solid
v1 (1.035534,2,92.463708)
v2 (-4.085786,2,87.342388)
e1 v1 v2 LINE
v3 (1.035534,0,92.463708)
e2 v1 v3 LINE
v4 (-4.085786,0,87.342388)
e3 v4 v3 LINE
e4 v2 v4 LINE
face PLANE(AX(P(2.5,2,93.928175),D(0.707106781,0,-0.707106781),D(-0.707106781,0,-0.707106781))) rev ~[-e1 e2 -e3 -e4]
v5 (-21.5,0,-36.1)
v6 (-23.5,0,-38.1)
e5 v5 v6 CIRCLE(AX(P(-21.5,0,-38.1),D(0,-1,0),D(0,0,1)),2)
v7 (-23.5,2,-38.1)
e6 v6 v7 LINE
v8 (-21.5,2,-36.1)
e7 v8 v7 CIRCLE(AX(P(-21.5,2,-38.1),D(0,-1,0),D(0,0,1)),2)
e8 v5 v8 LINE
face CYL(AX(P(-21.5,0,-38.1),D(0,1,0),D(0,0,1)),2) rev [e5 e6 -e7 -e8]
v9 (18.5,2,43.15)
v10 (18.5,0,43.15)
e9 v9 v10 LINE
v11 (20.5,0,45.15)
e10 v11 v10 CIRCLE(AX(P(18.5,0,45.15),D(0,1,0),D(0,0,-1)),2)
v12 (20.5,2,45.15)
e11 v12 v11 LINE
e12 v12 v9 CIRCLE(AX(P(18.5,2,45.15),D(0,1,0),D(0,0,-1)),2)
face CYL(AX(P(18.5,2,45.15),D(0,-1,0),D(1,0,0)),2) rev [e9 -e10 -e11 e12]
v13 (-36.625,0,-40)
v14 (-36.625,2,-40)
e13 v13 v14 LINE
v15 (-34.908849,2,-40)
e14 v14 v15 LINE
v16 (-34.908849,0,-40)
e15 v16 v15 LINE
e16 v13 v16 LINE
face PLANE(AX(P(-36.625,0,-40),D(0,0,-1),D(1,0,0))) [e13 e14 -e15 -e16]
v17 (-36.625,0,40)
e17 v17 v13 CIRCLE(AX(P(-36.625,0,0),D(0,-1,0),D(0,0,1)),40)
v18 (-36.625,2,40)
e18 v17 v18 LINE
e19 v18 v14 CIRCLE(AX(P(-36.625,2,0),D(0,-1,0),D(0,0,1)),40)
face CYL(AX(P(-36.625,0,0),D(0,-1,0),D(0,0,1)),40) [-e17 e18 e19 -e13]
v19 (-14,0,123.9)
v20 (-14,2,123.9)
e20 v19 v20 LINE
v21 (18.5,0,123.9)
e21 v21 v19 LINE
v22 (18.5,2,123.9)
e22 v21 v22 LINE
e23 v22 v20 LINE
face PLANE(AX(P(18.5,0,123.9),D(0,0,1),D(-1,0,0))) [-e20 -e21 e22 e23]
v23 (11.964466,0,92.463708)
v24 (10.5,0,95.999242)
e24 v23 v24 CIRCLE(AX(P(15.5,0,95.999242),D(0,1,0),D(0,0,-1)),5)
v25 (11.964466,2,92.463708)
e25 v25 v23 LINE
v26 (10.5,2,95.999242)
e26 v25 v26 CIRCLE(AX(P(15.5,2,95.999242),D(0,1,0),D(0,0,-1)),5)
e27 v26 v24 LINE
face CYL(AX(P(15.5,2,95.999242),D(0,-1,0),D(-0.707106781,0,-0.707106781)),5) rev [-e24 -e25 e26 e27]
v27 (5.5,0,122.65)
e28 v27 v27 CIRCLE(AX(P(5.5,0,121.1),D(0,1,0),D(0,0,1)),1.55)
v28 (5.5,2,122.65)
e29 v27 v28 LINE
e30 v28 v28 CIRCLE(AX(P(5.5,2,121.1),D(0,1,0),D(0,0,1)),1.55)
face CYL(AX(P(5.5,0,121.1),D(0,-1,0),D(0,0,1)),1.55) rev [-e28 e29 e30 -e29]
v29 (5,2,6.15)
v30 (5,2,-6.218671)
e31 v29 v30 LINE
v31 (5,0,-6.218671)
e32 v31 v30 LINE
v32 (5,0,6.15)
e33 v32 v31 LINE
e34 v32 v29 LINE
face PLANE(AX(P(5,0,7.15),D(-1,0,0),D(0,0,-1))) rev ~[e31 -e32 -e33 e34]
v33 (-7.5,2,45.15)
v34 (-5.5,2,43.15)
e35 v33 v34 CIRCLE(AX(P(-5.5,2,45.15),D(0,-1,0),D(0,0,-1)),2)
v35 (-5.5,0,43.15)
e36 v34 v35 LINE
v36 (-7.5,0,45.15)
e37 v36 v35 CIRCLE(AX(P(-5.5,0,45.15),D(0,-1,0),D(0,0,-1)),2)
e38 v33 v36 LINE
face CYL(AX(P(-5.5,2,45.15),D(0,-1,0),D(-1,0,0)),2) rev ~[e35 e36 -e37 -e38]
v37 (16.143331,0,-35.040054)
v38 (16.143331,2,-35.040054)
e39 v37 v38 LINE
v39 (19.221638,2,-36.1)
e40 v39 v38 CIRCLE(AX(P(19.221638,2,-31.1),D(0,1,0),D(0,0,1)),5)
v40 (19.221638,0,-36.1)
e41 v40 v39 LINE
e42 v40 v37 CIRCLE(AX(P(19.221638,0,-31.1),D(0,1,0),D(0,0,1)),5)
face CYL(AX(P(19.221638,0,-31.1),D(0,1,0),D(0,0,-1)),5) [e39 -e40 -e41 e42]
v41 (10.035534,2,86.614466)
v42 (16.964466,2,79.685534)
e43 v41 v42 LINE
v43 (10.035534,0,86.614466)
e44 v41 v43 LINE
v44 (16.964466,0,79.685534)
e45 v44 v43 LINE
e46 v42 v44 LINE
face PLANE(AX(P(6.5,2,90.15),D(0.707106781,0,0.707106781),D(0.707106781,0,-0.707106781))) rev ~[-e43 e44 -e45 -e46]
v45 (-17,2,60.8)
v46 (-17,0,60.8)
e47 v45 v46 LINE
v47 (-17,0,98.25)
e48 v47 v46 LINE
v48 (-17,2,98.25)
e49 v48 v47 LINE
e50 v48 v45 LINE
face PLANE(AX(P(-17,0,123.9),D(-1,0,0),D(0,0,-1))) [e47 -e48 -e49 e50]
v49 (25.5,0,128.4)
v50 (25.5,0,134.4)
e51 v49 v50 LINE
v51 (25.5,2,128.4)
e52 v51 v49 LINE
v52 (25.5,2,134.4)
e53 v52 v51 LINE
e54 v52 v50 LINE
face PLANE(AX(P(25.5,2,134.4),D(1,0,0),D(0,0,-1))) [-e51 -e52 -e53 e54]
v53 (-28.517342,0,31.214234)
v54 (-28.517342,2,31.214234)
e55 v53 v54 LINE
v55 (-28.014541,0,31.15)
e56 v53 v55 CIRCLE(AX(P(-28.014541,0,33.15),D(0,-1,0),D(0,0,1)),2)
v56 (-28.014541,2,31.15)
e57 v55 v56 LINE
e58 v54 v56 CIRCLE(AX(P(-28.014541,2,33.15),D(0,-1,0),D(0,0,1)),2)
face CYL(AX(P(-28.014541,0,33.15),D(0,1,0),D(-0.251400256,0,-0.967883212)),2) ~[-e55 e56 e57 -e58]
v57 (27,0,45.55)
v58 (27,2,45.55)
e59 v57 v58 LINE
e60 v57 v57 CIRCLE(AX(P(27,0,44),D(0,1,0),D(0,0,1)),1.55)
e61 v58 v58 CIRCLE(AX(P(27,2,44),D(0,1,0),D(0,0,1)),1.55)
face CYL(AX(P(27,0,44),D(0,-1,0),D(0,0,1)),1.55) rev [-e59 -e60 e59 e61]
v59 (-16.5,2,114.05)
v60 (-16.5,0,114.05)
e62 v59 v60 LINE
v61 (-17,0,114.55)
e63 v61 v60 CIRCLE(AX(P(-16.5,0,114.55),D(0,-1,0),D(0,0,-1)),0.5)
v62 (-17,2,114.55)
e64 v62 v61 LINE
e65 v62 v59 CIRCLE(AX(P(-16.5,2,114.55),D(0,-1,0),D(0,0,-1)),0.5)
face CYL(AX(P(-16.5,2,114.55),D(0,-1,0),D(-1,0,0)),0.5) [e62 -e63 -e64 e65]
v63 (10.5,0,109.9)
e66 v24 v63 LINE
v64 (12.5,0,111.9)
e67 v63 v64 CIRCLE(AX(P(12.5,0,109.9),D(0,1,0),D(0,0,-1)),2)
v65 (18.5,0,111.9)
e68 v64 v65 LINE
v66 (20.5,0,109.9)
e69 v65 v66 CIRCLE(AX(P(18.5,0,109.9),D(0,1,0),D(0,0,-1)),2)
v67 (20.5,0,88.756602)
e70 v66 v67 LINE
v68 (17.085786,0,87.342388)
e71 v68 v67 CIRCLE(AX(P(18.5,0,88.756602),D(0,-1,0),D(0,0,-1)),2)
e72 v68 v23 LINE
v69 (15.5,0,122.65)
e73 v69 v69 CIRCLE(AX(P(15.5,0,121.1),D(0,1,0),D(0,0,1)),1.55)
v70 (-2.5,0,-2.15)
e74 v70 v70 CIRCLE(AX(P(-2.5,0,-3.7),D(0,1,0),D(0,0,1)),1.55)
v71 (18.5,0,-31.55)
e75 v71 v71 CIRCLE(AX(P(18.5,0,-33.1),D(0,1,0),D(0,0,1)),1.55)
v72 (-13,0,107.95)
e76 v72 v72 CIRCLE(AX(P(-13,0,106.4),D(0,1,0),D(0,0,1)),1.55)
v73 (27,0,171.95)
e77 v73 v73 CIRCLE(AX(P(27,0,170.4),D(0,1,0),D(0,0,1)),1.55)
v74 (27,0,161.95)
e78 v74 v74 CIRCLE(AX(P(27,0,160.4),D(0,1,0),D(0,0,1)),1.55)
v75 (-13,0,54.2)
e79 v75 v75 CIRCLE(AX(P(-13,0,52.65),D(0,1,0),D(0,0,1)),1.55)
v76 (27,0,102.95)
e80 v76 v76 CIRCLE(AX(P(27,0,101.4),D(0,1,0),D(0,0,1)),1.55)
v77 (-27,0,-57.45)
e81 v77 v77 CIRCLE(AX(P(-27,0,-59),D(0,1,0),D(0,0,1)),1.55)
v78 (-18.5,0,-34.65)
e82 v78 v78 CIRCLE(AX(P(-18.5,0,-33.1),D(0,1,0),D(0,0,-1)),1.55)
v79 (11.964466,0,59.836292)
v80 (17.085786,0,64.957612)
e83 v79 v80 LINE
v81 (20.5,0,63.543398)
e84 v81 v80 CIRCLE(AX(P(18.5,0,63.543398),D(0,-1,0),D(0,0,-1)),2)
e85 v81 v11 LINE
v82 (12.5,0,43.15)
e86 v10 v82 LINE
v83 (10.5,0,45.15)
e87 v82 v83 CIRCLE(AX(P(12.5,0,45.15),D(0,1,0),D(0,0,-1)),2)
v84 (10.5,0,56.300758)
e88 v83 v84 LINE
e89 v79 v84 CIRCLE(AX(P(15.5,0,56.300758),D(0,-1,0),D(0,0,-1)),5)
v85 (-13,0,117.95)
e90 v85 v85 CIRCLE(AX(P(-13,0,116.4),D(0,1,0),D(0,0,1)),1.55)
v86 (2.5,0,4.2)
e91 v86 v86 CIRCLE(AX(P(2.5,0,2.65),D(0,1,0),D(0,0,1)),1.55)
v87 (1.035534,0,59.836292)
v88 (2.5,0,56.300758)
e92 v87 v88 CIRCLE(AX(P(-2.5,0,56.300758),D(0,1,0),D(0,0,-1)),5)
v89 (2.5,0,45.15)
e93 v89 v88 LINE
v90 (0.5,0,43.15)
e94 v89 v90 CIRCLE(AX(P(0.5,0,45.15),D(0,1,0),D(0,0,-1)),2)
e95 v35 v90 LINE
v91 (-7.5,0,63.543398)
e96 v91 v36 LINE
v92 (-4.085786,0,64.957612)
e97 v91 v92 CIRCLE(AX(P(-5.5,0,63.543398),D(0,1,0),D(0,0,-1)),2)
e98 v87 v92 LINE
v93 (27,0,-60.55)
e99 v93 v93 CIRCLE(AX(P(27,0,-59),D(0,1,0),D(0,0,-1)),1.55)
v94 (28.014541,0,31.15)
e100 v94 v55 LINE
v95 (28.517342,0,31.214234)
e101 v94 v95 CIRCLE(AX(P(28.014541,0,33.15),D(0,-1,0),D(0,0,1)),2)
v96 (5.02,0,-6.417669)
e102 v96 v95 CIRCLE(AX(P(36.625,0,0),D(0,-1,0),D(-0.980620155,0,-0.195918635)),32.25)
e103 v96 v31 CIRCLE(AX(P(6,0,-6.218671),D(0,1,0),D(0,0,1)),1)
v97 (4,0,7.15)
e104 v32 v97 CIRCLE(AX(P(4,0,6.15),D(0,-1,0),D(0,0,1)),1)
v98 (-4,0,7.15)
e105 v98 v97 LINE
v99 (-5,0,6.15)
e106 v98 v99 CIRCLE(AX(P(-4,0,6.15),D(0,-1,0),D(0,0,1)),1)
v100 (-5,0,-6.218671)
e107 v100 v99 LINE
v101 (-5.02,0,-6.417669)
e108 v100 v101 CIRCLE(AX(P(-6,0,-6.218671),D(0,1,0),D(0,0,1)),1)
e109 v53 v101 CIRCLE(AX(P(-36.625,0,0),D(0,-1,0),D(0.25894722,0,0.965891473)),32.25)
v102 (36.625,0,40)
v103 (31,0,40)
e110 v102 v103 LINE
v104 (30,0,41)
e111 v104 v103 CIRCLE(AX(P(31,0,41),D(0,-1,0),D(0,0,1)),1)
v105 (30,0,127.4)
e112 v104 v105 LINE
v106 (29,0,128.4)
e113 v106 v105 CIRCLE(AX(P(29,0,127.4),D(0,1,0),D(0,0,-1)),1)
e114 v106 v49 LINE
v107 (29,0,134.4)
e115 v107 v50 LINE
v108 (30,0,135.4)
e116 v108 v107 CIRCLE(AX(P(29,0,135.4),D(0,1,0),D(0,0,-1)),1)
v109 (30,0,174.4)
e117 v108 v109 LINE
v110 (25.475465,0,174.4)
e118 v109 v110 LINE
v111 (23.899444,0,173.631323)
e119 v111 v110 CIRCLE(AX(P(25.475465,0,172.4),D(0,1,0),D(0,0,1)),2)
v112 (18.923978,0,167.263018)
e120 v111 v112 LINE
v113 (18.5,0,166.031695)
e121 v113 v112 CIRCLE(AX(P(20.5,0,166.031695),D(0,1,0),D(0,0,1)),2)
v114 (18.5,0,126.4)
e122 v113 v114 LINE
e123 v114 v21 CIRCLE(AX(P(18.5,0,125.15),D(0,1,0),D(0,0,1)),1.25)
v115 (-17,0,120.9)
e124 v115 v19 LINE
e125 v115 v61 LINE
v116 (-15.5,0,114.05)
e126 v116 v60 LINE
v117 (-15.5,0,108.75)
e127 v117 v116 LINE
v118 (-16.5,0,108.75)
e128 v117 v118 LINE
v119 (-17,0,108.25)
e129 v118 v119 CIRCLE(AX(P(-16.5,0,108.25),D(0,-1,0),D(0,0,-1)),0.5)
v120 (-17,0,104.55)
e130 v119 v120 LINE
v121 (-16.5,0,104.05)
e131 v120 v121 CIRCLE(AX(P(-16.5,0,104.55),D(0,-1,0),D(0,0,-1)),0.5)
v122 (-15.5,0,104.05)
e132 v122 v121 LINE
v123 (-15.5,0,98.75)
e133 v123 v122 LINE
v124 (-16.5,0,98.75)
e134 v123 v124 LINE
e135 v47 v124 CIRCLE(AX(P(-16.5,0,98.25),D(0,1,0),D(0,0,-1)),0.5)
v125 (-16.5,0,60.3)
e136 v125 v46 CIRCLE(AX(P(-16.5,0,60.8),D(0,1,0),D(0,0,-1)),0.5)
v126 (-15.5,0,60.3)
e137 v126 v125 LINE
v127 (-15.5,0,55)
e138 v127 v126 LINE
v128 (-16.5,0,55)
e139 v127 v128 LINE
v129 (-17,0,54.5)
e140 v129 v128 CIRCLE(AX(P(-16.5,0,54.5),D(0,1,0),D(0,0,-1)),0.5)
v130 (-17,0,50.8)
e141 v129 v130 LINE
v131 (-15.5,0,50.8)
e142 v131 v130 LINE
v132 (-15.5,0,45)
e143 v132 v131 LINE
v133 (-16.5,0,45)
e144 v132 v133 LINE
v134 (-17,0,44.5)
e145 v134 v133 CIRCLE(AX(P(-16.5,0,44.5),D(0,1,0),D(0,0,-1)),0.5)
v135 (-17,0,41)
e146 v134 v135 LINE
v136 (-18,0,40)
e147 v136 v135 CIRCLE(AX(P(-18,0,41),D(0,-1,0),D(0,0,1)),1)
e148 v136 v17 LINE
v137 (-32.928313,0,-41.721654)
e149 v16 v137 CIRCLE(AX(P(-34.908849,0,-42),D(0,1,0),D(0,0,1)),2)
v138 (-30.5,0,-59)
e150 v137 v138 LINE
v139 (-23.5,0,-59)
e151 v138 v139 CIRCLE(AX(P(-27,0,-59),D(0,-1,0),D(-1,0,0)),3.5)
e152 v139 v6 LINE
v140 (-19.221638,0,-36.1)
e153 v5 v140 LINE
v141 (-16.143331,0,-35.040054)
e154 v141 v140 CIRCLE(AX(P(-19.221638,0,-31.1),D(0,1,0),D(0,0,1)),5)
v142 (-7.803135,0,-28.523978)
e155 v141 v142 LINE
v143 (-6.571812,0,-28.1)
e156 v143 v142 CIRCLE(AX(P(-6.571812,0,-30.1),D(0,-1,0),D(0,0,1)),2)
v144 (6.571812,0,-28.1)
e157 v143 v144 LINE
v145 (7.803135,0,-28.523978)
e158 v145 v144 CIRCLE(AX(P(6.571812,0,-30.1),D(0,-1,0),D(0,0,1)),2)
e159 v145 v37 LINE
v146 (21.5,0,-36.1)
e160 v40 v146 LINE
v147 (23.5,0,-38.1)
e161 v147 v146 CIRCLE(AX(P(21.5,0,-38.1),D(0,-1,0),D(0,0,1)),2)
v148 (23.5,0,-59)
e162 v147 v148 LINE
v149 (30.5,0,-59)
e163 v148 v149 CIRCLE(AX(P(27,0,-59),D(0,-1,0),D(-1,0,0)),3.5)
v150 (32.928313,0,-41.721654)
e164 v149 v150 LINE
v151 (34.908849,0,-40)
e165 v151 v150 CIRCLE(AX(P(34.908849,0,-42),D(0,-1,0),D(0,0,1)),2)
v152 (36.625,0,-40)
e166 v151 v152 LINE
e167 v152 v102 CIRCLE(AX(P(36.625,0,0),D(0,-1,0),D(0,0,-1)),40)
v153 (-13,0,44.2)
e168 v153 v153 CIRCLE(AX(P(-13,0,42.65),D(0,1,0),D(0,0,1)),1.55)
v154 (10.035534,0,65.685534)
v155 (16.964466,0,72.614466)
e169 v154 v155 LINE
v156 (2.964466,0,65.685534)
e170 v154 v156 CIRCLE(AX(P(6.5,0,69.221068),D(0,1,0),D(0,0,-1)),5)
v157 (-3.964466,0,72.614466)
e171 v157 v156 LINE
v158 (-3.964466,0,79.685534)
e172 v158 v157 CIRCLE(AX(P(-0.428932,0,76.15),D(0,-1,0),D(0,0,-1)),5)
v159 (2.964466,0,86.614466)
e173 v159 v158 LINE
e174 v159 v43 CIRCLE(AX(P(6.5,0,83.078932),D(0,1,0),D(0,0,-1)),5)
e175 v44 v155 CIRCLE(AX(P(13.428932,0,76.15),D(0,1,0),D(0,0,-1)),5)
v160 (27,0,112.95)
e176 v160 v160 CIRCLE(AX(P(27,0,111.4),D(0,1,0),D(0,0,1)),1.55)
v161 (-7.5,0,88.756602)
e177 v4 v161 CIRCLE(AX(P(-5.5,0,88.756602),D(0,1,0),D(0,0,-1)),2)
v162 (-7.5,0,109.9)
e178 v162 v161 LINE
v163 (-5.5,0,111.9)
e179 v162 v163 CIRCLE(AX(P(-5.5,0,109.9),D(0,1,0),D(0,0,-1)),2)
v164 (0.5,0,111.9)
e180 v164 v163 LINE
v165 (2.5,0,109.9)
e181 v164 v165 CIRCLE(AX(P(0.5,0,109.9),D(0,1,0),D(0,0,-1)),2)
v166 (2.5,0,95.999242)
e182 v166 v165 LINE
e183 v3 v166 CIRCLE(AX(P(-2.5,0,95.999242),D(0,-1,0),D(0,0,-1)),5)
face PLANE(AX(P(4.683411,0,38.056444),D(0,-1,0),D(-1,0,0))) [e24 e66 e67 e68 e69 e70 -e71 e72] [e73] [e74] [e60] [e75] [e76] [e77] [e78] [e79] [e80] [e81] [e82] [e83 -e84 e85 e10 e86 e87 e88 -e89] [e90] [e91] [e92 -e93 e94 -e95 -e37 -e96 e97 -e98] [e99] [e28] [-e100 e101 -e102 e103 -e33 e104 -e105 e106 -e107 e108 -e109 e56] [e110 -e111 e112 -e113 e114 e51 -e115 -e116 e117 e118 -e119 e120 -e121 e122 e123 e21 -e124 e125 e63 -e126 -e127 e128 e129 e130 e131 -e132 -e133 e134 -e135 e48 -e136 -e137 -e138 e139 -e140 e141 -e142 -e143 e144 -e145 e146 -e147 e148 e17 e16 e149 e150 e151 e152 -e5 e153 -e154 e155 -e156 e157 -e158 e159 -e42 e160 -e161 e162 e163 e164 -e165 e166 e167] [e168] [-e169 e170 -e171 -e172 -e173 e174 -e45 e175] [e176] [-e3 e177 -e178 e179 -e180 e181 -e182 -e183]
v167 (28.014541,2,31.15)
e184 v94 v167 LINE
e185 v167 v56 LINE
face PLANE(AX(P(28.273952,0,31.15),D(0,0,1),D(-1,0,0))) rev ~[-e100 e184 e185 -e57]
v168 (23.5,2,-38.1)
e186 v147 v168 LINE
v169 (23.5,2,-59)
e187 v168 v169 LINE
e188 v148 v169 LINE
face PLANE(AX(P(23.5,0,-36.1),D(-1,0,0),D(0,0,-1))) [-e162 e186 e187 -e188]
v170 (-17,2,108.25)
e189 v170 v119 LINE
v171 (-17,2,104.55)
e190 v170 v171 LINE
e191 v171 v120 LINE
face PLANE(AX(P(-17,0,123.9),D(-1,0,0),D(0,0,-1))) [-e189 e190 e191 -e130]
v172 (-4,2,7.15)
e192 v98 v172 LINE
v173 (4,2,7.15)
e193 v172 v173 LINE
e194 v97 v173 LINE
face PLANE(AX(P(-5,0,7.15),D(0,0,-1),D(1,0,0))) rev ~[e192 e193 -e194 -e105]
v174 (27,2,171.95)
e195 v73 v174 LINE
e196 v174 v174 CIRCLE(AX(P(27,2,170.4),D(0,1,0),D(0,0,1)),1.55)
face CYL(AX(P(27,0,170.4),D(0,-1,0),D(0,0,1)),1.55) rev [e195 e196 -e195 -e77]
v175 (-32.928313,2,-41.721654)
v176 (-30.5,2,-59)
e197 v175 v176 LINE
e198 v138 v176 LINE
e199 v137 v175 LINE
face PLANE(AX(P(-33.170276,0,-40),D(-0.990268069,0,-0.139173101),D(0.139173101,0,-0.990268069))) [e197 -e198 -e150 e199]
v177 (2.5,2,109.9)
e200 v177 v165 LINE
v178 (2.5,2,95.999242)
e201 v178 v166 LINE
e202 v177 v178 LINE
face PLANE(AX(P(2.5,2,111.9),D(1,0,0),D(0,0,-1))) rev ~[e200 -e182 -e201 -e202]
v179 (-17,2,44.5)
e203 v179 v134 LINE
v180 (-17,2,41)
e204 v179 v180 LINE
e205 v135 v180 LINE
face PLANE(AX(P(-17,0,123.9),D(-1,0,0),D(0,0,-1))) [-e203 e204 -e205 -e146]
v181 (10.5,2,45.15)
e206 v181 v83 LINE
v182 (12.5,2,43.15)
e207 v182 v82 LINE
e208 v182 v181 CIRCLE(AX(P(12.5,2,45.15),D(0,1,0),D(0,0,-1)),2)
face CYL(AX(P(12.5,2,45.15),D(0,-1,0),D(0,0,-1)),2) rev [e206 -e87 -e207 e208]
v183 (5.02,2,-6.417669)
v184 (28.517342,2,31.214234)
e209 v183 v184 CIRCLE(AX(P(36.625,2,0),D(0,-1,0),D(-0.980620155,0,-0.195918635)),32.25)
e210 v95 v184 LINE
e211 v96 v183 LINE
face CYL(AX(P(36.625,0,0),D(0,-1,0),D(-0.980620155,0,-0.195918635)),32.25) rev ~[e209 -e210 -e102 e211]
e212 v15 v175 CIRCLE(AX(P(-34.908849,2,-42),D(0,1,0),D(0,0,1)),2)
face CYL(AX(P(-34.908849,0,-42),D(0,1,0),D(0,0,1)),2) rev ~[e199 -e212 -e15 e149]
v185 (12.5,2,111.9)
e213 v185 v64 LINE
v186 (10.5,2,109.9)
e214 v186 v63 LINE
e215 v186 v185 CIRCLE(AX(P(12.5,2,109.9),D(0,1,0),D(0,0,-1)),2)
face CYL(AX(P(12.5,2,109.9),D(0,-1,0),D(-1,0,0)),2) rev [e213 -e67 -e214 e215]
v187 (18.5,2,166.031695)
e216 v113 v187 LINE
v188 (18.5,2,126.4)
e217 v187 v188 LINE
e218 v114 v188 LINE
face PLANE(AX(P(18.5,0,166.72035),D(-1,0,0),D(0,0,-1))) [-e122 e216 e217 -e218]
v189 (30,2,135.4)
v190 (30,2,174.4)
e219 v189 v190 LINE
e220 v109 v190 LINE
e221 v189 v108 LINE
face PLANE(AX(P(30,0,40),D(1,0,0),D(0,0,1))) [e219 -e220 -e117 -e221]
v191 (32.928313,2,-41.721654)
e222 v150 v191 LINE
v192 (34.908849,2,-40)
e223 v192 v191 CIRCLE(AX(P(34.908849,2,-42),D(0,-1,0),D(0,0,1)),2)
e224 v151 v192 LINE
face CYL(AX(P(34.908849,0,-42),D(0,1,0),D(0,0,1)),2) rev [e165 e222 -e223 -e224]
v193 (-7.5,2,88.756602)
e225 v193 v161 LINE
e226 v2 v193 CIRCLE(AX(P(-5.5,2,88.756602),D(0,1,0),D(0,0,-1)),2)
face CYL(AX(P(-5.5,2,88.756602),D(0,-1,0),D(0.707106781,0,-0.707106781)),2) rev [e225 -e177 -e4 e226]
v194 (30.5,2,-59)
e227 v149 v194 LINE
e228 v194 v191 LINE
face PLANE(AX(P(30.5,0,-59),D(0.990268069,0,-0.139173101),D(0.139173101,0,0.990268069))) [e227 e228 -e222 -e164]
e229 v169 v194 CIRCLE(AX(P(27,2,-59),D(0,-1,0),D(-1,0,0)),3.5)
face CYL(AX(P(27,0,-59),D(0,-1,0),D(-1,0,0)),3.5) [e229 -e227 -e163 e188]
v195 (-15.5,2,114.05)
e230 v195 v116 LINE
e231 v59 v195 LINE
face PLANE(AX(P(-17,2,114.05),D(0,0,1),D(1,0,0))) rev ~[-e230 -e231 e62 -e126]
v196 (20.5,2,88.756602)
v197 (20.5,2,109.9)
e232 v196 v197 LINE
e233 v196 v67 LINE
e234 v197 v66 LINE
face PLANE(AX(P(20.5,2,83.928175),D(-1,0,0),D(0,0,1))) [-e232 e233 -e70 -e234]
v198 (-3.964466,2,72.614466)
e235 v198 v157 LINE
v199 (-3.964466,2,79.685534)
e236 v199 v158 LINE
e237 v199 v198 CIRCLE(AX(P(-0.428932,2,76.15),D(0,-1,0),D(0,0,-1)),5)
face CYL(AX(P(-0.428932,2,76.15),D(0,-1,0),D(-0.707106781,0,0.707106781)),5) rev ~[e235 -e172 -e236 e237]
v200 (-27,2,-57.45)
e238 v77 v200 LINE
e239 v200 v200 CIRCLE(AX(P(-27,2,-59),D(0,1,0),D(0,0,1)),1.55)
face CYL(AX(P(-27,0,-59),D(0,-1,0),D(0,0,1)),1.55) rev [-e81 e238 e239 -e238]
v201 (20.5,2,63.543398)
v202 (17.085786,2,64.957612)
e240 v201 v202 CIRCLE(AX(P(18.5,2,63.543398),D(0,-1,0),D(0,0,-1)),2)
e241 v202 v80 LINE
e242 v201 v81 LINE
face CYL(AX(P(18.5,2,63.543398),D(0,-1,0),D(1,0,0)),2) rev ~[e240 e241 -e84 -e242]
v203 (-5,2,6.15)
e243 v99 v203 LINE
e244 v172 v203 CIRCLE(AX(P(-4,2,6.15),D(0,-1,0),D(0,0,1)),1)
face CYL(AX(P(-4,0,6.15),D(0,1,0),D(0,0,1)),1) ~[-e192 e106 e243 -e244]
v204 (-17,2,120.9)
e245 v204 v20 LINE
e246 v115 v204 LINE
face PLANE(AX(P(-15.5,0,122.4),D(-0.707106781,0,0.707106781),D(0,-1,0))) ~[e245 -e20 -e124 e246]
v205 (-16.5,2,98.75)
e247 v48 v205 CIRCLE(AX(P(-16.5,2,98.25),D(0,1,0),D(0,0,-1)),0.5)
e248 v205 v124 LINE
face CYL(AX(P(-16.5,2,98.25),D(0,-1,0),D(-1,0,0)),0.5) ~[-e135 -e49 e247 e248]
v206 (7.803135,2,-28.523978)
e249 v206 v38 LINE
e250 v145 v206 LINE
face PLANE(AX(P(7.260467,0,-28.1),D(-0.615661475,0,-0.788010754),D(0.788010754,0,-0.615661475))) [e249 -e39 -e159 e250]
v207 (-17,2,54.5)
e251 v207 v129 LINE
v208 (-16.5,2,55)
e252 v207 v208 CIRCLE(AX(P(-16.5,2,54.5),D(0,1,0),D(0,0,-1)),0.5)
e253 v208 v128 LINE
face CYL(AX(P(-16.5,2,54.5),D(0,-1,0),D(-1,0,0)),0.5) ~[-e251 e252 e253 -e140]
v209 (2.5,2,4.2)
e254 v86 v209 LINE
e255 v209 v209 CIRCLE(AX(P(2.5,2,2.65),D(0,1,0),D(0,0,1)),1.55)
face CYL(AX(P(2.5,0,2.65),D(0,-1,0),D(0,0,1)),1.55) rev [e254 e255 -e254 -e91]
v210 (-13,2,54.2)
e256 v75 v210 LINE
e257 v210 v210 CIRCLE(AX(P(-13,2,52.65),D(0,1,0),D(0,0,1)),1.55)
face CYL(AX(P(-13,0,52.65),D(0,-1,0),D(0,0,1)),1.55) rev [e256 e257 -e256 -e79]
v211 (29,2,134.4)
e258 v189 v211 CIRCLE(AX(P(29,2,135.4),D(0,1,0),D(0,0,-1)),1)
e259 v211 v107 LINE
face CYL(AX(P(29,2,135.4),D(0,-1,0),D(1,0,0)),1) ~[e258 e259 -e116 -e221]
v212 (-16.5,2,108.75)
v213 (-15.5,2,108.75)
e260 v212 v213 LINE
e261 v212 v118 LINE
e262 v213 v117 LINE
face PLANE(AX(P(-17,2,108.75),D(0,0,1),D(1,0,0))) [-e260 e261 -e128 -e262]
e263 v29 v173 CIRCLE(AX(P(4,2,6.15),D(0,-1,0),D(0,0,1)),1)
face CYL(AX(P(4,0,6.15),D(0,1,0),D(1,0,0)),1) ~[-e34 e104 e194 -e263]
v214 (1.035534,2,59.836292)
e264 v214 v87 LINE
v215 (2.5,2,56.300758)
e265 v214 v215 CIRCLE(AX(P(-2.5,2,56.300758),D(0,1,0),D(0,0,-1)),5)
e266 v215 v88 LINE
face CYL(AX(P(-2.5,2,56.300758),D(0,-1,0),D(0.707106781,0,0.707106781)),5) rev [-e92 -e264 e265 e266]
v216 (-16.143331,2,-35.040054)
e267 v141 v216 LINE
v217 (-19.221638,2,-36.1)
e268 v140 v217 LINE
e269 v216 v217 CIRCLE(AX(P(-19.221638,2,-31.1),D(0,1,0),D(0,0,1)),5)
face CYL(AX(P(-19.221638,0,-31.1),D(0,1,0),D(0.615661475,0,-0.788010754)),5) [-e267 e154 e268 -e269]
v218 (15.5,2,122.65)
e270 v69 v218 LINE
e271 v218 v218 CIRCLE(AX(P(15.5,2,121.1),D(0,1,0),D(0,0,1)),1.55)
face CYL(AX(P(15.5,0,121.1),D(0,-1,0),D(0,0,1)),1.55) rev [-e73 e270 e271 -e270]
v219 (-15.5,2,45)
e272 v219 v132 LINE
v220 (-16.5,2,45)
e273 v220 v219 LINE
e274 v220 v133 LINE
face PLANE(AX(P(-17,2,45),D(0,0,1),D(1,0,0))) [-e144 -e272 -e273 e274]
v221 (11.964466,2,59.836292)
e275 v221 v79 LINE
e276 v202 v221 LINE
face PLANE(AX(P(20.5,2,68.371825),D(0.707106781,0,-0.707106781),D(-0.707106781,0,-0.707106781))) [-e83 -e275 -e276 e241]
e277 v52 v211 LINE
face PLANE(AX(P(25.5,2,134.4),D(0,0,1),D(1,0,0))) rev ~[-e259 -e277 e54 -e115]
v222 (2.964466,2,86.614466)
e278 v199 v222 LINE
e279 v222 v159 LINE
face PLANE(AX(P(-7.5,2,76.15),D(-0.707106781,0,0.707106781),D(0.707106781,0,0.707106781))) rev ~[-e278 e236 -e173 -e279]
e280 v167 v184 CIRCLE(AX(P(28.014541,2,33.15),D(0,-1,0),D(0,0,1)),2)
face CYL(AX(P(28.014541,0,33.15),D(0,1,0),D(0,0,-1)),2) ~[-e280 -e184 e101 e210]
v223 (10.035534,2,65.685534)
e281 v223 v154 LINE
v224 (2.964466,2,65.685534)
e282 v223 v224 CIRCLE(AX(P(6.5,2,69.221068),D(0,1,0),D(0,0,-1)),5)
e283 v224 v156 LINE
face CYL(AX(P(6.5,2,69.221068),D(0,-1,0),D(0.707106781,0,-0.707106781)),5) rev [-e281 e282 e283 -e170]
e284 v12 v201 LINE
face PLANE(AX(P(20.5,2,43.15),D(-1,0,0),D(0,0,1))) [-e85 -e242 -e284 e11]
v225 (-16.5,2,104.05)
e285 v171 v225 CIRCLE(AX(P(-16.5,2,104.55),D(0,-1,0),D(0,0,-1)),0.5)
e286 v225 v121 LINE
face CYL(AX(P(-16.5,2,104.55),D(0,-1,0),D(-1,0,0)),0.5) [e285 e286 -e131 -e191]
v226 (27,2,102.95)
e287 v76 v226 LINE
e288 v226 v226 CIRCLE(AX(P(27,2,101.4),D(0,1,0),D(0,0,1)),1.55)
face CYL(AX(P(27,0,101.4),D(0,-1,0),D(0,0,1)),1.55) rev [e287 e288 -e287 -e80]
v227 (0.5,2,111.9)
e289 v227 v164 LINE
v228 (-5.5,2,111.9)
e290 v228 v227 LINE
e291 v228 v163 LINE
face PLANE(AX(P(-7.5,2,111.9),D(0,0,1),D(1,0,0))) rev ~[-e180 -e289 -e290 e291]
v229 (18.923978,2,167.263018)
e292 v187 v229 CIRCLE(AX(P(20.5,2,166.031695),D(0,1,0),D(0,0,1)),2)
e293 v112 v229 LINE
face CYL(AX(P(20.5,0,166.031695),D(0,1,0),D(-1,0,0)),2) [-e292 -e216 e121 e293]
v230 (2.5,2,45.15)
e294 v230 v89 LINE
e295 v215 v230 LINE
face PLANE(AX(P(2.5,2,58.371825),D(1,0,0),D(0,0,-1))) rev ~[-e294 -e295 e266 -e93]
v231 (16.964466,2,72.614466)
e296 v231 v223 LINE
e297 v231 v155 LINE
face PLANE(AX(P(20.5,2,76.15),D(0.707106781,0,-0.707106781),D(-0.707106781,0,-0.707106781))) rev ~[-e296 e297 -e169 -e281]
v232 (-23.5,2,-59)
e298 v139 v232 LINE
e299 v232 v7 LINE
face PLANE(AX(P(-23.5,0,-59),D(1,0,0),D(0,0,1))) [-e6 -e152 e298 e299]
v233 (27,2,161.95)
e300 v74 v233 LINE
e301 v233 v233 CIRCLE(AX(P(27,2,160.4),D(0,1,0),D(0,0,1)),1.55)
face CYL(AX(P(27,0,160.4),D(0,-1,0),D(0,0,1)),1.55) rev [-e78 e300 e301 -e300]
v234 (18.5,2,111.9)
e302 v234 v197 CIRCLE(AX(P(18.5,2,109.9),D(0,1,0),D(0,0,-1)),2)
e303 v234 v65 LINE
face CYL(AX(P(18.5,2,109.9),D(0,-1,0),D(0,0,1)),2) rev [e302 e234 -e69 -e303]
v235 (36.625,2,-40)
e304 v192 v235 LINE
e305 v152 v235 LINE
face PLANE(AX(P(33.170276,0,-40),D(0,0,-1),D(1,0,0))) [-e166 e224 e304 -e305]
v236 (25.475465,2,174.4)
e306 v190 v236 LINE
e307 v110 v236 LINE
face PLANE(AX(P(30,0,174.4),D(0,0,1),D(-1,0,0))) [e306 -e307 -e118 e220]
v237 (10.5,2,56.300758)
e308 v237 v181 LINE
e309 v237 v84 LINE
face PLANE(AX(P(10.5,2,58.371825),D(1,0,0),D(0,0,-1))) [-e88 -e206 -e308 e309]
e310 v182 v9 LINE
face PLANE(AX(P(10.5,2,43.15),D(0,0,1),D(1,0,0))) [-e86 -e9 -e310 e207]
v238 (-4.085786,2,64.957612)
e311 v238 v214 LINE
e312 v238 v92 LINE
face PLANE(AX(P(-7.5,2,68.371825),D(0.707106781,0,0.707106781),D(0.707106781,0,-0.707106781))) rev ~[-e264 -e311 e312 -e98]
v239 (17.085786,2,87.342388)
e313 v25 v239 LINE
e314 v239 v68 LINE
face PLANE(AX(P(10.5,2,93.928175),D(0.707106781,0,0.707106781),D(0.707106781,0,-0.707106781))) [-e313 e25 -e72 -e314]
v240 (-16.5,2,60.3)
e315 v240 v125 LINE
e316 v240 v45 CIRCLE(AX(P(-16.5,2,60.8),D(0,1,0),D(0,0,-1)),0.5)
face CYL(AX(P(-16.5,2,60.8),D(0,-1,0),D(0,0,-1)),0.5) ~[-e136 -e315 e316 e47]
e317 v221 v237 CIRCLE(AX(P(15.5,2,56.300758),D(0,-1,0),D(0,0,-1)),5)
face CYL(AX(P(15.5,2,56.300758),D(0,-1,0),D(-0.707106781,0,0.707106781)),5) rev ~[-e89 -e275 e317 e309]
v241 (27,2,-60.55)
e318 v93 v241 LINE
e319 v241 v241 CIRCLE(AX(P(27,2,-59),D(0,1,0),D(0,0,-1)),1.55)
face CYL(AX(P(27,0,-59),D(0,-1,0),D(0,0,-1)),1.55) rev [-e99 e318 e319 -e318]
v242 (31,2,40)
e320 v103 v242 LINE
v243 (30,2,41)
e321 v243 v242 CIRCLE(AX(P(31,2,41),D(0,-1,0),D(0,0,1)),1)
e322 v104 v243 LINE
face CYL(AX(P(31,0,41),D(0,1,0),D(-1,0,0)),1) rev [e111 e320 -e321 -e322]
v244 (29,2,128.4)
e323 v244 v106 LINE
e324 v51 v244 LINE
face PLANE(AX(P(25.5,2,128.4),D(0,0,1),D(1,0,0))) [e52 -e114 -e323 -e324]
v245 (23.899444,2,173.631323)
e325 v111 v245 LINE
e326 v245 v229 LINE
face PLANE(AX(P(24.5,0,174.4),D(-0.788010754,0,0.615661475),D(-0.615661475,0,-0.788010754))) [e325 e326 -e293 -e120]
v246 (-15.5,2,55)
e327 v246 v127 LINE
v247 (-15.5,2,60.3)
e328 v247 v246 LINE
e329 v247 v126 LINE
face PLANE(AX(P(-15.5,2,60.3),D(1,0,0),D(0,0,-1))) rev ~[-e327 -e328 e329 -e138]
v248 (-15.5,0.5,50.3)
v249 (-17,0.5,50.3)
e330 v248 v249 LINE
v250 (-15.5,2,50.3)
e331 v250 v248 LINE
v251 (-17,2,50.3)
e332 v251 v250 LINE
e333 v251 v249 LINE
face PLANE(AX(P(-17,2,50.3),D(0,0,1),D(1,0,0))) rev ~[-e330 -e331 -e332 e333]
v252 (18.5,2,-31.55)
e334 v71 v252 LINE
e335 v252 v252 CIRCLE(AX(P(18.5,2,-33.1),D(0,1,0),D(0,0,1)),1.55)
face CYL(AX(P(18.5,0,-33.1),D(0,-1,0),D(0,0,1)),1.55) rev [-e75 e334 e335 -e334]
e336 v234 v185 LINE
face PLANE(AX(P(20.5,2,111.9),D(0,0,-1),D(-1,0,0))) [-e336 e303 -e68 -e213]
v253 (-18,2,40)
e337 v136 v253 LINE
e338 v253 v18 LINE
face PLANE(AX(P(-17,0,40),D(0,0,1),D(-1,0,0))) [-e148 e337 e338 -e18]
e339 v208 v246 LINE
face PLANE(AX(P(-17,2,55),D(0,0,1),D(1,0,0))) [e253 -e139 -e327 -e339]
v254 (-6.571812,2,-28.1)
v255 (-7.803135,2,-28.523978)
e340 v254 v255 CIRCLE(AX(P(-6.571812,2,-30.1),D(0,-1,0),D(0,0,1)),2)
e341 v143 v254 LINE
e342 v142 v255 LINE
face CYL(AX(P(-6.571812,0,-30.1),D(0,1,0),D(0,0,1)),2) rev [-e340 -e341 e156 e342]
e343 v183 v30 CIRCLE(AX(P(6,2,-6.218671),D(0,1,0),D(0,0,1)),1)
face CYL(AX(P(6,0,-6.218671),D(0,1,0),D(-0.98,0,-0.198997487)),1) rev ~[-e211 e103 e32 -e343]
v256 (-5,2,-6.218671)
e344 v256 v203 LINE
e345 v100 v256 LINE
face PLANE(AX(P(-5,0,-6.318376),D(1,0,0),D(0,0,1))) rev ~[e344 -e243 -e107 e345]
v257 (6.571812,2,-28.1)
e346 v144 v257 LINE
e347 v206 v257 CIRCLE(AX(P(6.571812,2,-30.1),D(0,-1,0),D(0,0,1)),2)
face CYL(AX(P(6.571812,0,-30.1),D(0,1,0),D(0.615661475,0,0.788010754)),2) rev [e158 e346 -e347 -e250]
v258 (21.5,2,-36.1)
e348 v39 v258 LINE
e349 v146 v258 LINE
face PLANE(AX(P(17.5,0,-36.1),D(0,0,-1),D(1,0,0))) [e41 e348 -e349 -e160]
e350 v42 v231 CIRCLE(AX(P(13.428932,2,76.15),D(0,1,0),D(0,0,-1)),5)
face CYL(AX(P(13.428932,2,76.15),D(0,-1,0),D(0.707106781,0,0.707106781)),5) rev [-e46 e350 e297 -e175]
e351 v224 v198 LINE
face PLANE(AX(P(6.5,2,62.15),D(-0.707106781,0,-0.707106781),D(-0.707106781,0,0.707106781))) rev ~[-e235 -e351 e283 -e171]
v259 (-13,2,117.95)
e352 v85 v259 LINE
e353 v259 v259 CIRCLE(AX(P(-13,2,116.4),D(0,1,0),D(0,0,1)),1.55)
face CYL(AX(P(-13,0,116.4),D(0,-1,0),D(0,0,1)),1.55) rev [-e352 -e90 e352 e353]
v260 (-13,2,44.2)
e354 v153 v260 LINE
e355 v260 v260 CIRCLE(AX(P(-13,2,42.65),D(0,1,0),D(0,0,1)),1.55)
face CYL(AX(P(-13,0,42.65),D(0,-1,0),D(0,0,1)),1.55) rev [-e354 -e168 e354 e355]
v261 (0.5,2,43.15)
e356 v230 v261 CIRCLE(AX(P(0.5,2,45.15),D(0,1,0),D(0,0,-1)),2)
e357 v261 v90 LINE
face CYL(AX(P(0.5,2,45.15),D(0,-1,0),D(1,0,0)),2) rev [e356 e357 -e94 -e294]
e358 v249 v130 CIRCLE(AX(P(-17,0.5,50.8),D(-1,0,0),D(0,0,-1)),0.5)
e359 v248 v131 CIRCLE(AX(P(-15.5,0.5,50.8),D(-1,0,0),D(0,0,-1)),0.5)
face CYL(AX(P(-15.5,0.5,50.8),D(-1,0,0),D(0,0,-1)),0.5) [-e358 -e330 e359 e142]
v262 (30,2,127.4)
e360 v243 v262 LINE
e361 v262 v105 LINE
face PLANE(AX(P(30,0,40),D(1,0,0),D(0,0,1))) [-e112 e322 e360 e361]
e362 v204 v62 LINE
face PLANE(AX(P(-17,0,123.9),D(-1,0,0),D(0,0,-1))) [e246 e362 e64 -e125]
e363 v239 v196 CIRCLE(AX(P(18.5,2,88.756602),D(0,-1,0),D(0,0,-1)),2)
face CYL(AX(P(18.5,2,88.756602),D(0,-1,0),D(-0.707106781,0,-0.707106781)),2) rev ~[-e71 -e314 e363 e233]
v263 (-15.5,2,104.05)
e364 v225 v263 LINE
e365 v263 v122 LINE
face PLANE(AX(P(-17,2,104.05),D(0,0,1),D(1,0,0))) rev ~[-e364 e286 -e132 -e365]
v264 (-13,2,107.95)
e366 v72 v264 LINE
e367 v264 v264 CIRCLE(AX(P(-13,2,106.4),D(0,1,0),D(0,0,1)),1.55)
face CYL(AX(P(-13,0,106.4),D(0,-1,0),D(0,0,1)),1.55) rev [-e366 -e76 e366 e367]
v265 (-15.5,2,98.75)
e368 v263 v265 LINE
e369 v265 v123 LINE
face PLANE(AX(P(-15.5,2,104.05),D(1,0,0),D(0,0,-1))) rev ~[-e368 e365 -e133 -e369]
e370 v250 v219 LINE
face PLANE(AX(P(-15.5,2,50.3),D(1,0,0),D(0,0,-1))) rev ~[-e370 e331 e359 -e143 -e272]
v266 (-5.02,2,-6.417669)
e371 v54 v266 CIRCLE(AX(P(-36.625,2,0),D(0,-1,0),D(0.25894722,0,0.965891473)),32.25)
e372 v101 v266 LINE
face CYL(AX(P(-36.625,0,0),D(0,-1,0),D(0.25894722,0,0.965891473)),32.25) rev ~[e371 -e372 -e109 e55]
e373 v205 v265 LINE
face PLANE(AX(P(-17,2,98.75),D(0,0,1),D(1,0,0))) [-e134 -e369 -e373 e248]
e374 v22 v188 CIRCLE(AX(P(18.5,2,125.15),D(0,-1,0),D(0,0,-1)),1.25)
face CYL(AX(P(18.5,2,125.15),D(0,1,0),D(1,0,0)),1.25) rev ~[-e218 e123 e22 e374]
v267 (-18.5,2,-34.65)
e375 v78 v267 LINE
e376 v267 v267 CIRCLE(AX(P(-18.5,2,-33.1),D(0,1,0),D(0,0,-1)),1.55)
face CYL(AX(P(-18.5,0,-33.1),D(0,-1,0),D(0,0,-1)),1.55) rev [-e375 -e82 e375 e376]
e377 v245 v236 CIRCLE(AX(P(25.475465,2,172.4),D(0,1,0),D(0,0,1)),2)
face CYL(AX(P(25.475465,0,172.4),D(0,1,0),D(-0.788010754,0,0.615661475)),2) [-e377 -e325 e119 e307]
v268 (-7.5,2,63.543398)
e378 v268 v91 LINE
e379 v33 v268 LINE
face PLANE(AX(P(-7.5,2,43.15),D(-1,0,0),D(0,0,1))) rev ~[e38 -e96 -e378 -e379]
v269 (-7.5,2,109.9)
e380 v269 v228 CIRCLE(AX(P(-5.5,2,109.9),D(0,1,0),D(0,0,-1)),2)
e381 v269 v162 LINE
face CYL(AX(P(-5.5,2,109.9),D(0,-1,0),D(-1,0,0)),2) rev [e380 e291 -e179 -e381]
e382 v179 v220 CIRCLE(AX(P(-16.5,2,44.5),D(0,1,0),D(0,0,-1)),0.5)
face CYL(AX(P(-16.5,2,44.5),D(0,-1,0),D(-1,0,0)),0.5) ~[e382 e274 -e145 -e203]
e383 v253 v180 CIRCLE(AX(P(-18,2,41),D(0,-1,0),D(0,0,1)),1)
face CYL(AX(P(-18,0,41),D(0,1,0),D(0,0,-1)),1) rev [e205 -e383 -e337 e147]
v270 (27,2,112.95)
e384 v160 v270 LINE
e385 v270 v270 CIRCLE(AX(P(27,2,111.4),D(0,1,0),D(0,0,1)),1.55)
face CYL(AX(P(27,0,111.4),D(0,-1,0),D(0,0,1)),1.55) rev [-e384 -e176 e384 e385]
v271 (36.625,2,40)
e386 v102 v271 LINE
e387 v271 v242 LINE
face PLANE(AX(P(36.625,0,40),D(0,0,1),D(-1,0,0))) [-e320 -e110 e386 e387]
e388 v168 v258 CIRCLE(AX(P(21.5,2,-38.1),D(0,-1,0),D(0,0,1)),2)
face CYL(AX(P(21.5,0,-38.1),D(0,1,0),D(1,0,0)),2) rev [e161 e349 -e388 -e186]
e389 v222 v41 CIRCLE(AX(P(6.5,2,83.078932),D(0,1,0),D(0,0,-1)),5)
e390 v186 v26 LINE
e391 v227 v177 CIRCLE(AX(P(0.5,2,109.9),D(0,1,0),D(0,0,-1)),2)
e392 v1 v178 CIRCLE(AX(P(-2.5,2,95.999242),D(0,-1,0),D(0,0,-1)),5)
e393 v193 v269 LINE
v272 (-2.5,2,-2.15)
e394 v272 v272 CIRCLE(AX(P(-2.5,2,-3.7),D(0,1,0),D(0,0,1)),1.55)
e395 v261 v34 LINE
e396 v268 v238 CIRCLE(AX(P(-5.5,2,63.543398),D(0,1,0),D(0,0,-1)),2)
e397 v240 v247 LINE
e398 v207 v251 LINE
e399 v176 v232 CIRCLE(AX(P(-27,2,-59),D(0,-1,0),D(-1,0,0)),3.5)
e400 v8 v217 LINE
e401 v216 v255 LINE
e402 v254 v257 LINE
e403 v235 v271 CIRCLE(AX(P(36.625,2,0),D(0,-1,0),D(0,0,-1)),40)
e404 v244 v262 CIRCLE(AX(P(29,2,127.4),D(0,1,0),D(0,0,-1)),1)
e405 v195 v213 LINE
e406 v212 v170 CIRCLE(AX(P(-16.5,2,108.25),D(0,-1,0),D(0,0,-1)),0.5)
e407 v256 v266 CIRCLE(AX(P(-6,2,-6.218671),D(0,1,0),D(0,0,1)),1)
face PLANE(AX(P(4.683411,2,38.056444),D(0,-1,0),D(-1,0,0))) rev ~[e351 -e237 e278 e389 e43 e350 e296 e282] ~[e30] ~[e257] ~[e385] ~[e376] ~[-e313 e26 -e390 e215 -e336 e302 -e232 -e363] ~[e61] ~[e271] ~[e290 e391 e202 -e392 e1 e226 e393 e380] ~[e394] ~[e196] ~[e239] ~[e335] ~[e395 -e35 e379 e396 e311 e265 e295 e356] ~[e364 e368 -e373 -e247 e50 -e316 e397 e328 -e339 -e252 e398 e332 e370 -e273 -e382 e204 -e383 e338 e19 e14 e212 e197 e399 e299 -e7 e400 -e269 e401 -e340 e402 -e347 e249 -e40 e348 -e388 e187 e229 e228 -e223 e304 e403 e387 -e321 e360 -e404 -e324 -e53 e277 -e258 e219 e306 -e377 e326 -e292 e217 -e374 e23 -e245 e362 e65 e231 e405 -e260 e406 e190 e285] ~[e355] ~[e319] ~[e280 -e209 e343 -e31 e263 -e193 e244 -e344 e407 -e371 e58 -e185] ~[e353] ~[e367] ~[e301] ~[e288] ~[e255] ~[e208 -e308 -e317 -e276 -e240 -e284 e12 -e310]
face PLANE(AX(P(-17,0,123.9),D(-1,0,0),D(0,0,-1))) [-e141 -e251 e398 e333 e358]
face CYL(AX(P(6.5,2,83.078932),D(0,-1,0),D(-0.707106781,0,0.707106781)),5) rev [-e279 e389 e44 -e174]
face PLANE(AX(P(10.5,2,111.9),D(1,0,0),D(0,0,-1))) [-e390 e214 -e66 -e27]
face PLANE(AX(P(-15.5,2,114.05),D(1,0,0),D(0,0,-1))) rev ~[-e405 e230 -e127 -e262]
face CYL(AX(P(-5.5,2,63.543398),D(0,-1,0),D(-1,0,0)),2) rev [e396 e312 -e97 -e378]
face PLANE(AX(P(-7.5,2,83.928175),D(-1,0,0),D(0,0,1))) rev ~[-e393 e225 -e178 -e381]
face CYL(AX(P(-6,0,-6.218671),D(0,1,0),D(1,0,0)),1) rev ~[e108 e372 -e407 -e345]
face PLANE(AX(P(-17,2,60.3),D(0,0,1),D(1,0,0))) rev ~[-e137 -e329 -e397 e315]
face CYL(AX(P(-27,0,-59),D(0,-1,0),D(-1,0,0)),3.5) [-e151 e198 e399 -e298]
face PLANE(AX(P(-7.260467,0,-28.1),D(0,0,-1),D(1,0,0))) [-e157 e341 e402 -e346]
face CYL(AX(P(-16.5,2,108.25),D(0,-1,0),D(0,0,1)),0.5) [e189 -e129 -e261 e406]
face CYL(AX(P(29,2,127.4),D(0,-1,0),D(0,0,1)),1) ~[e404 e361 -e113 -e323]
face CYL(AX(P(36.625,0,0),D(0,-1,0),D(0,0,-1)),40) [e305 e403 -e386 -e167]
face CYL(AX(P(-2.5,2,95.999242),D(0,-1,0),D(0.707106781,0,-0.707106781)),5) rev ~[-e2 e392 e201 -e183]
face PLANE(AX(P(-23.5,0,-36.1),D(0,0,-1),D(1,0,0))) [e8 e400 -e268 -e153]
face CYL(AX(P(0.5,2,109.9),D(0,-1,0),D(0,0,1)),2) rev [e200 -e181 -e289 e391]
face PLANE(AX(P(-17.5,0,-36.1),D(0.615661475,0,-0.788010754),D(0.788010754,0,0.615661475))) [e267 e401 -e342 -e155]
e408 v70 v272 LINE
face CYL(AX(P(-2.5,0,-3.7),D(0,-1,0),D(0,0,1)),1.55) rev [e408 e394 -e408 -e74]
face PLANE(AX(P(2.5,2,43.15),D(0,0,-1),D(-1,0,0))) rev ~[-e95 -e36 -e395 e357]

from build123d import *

# Parameters (mm, degrees)
SKETCH_1_R          = 1.55
EXTRUDE_1_DEPTH     = 2
SKETCH_3_R          = 1.25
SKETCH_3_W          = 1.5
SKETCH_3_H          = 5.3
SKETCH_3_W_2        = 4.5
SKETCH_3_H_2        = 6
CUT_EXTRUDE_1_DEPTH = 3.2
CHAMFER_1_SIZE      = 3
FILLET_1_R          = 2
FILLET_2_R          = 5
FILLET_3_R          = 0.5
FILLET_4_R          = 1


with BuildPart() as part:
    # 草图1 → 凸台-拉伸1 (new body)
    with BuildSketch(Plane(origin=(0, 0, 0), x_dir=(1, 0, 0), z_dir=(0, 1, 0))):
        with BuildLine():
            Line((17.5, 36.1), (23.5, 36.1))
            Line((23.5, 36.1), (23.5, 59))
            ThreePointArc((23.5, 59), (27, 62.5), (30.5, 59))
            Line((30.5, 59), (33.170275859, 40))
            Line((33.170275859, 40), (36.625, 40))
            ThreePointArc((36.625, 40), (76.625, 0), (36.625, -40))
            Line((36.625, -40), (30, -40))
            Line((30, -40), (30, -123.9))
            Line((30, -123.9), (30, -174.4))
            Line((30, -174.4), (24.5, -174.4))
            Line((24.5, -174.4), (18.5, -166.720350207))
            Line((18.5, -166.720350207), (18.5, -123.9))
            Line((18.5, -123.9), (-17, -123.9))
            Line((-17, -123.9), (-17, -40))
            Line((-17, -40), (-36.625, -40))
            ThreePointArc((-36.625, -40), (-76.625, 0), (-36.625, 40))
            Line((-36.625, 40), (-33.170275859, 40))
            Line((-33.170275859, 40), (-30.5, 59))
            ThreePointArc((-30.5, 59), (-27, 62.5), (-23.5, 59))
            Line((-23.5, 59), (-23.5, 36.1))
            Line((-23.5, 36.1), (-17.5, 36.1))
            Line((-17.5, 36.1), (-7.260466942, 28.1))
            Line((-7.260466942, 28.1), (7.260466942, 28.1))
            Line((7.260466942, 28.1), (17.5, 36.1))
        make_face()
        with Locations(Location((18.5, 33.1, 0), (0, 0, 270))):
            Circle(SKETCH_1_R, mode=Mode.SUBTRACT)
        with Locations(Location((-18.5, 33.1, 0), (0, 0, 90))):
            Circle(SKETCH_1_R, mode=Mode.SUBTRACT)
        with Locations(Location((27, -44, 0), (0, 0, 270))):
            Circle(SKETCH_1_R, mode=Mode.SUBTRACT)
        with Locations(Location((27, -101.4, 0), (0, 0, 270))):
            Circle(SKETCH_1_R, mode=Mode.SUBTRACT)
        with Locations(Location((27, -111.4, 0), (0, 0, 270))):
            Circle(SKETCH_1_R, mode=Mode.SUBTRACT)
        with Locations(Location((-13, -42.65, 0), (0, 0, 270))):
            Circle(SKETCH_1_R, mode=Mode.SUBTRACT)
        with Locations(Location((-13, -52.65, 0), (0, 0, 270))):
            Circle(SKETCH_1_R, mode=Mode.SUBTRACT)
        with Locations(Location((-13, -106.4, 0), (0, 0, 270))):
            Circle(SKETCH_1_R, mode=Mode.SUBTRACT)
        with Locations(Location((-13, -116.4, 0), (0, 0, 270))):
            Circle(SKETCH_1_R, mode=Mode.SUBTRACT)
        with Locations(Location((5.5, -121.1, 0), (0, 0, 270))):
            Circle(SKETCH_1_R, mode=Mode.SUBTRACT)
        with Locations(Location((15.5, -121.1, 0), (0, 0, 270))):
            Circle(SKETCH_1_R, mode=Mode.SUBTRACT)
        with Locations(Location((27, -160.4, 0), (0, 0, 270))):
            Circle(SKETCH_1_R, mode=Mode.SUBTRACT)
        with Locations(Location((27, -170.4, 0), (0, 0, 270))):
            Circle(SKETCH_1_R, mode=Mode.SUBTRACT)
        with Locations(Location((-2.5, 3.7, 0), (0, 0, 270))):
            Circle(SKETCH_1_R, mode=Mode.SUBTRACT)
        with Locations(Location((2.5, -2.65, 0), (0, 0, 270))):
            Circle(SKETCH_1_R, mode=Mode.SUBTRACT)
        with Locations(Location((-27, 59, 0), (0, 0, 270))):
            Circle(SKETCH_1_R, mode=Mode.SUBTRACT)
        with Locations(Location((27, 59, 0), (0, 0, 90))):
            Circle(SKETCH_1_R, mode=Mode.SUBTRACT)
        with BuildLine():
            Line((-5, 6.318375978), (-5, -7.15))
            Line((-5, -7.15), (5, -7.15))
            Line((5, -7.15), (5, 6.318375978))
            ThreePointArc((5, 6.318375978), (64.020088972, 17.016803466), (28.273952162, -31.15))
            Line((28.273952162, -31.15), (-28.273952162, -31.15))
            ThreePointArc((-28.273952162, -31.15), (-64.020088972, 17.016803466), (-5, 6.318375978))
        make_face(mode=Mode.SUBTRACT)
    extrude(amount=EXTRUDE_1_DEPTH)

    # 草图3 → 切除-拉伸1 (cut)
    with BuildSketch(Plane(origin=(0, 2, 0), x_dir=(1, 0, 0), z_dir=(0, 1, 0))):
        with Locations((18.5, -125.15)):
            Circle(SKETCH_3_R)
        with Locations((-16.25, -47.65)):
            Rectangle(SKETCH_3_W, SKETCH_3_H)
        with Locations((-16.25, -57.65)):
            Rectangle(SKETCH_3_W, SKETCH_3_H)
        with Locations((-16.25, -101.4)):
            Rectangle(SKETCH_3_W, SKETCH_3_H)
        with Locations((-16.25, -111.4)):
            Rectangle(SKETCH_3_W, SKETCH_3_H)
        with Locations((27.75, -131.4)):
            Rectangle(SKETCH_3_W_2, SKETCH_3_H_2)
        Polygon((6.5, -90.15), (20.5, -76.15), (6.5, -62.15), (-7.5, -76.15), align=None)
        Polygon((-7.5, -68.371825407), (2.5, -58.371825407), (2.5, -43.15), (-7.5, -43.15), align=None)
        Polygon((-7.5, -83.928174593), (-7.5, -111.9), (2.5, -111.9), (2.5, -93.928174593), align=None)
        Polygon((10.5, -93.928174593), (20.5, -83.928174593), (20.5, -111.9), (10.5, -111.9), align=None)
        Polygon((20.5, -43.15), (20.5, -68.371825407), (10.5, -58.371825407), (10.5, -43.15), align=None)
    extrude(amount=-CUT_EXTRUDE_1_DEPTH, mode=Mode.SUBTRACT)

    # 倒角1
    chamfer_1_edges = [part.edges().sort_by_distance(p)[0] for p in [
        (-17, 1, 123.9),
    ]]
    chamfer(chamfer_1_edges, length=CHAMFER_1_SIZE)

    # 圆角1
    fillet_1_edges = [part.edges().sort_by_distance(p)[0] for p in [
        (-7.5, 1, 43.15),
        (2.5, 1, 43.15),
        (-7.5, 1, 68.371825407),
        (2.5, 1, 111.9),
        (-7.5, 1, 111.9),
        (-7.5, 1, 83.928174593),
        (10.5, 1, 111.9),
        (20.5, 1, 83.928174593),
        (20.5, 1, 111.9),
        (10.5, 1, 43.15),
        (20.5, 1, 43.15),
        (20.5, 1, 68.371825407),
        (23.5, 1, -36.1),
        (33.170275859, 1, -40),
        (24.5, 1, 174.4),
        (18.5, 1, 166.720350207),
        (-33.170275859, 1, -40),
        (-23.5, 1, -36.1),
        (-7.260466942, 1, -28.1),
        (7.260466942, 1, -28.1),
        (-28.273952162, 1, 31.15),
        (28.273952162, 1, 31.15),
    ]]
    fillet(fillet_1_edges, radius=FILLET_1_R)

    # 圆角2
    fillet_2_edges = [part.edges().sort_by_distance(p)[0] for p in [
        (6.5, 1, 90.15),
        (-7.5, 1, 76.15),
        (6.5, 1, 62.15),
        (20.5, 1, 76.15),
        (2.5, 1, 58.371825407),
        (2.5, 1, 93.928174593),
        (10.5, 1, 93.928174593),
        (10.5, 1, 58.371825407),
        (17.5, 1, -36.1),
        (-17.5, 1, -36.1),
    ]]
    fillet(fillet_2_edges, radius=FILLET_2_R)

    # 圆角3
    fillet_3_edges = [part.edges().sort_by_distance(p)[0] for p in [
        (-17, 1, 45),
        (-17, 1, 60.3),
        (-17, 1, 55),
        (-17, 1, 104.05),
        (-17, 1, 98.75),
        (-17, 1, 114.05),
        (-17, 1, 108.75),
        (-16.25, 0, 50.3),
    ]]
    fillet(fillet_3_edges, radius=FILLET_3_R)

    # 圆角4
    fillet_4_edges = [part.edges().sort_by_distance(p)[0] for p in [
        (30, 1, 128.4),
        (30, 1, 134.4),
        (30, 1, 40),
        (-17, 1, 40),
        (-5, 1, -6.318375978),
        (5, 1, -6.318375978),
        (5, 1, 7.15),
        (-5, 1, 7.15),
    ]]
    fillet(fillet_4_edges, radius=FILLET_4_R)


solid = part.part
